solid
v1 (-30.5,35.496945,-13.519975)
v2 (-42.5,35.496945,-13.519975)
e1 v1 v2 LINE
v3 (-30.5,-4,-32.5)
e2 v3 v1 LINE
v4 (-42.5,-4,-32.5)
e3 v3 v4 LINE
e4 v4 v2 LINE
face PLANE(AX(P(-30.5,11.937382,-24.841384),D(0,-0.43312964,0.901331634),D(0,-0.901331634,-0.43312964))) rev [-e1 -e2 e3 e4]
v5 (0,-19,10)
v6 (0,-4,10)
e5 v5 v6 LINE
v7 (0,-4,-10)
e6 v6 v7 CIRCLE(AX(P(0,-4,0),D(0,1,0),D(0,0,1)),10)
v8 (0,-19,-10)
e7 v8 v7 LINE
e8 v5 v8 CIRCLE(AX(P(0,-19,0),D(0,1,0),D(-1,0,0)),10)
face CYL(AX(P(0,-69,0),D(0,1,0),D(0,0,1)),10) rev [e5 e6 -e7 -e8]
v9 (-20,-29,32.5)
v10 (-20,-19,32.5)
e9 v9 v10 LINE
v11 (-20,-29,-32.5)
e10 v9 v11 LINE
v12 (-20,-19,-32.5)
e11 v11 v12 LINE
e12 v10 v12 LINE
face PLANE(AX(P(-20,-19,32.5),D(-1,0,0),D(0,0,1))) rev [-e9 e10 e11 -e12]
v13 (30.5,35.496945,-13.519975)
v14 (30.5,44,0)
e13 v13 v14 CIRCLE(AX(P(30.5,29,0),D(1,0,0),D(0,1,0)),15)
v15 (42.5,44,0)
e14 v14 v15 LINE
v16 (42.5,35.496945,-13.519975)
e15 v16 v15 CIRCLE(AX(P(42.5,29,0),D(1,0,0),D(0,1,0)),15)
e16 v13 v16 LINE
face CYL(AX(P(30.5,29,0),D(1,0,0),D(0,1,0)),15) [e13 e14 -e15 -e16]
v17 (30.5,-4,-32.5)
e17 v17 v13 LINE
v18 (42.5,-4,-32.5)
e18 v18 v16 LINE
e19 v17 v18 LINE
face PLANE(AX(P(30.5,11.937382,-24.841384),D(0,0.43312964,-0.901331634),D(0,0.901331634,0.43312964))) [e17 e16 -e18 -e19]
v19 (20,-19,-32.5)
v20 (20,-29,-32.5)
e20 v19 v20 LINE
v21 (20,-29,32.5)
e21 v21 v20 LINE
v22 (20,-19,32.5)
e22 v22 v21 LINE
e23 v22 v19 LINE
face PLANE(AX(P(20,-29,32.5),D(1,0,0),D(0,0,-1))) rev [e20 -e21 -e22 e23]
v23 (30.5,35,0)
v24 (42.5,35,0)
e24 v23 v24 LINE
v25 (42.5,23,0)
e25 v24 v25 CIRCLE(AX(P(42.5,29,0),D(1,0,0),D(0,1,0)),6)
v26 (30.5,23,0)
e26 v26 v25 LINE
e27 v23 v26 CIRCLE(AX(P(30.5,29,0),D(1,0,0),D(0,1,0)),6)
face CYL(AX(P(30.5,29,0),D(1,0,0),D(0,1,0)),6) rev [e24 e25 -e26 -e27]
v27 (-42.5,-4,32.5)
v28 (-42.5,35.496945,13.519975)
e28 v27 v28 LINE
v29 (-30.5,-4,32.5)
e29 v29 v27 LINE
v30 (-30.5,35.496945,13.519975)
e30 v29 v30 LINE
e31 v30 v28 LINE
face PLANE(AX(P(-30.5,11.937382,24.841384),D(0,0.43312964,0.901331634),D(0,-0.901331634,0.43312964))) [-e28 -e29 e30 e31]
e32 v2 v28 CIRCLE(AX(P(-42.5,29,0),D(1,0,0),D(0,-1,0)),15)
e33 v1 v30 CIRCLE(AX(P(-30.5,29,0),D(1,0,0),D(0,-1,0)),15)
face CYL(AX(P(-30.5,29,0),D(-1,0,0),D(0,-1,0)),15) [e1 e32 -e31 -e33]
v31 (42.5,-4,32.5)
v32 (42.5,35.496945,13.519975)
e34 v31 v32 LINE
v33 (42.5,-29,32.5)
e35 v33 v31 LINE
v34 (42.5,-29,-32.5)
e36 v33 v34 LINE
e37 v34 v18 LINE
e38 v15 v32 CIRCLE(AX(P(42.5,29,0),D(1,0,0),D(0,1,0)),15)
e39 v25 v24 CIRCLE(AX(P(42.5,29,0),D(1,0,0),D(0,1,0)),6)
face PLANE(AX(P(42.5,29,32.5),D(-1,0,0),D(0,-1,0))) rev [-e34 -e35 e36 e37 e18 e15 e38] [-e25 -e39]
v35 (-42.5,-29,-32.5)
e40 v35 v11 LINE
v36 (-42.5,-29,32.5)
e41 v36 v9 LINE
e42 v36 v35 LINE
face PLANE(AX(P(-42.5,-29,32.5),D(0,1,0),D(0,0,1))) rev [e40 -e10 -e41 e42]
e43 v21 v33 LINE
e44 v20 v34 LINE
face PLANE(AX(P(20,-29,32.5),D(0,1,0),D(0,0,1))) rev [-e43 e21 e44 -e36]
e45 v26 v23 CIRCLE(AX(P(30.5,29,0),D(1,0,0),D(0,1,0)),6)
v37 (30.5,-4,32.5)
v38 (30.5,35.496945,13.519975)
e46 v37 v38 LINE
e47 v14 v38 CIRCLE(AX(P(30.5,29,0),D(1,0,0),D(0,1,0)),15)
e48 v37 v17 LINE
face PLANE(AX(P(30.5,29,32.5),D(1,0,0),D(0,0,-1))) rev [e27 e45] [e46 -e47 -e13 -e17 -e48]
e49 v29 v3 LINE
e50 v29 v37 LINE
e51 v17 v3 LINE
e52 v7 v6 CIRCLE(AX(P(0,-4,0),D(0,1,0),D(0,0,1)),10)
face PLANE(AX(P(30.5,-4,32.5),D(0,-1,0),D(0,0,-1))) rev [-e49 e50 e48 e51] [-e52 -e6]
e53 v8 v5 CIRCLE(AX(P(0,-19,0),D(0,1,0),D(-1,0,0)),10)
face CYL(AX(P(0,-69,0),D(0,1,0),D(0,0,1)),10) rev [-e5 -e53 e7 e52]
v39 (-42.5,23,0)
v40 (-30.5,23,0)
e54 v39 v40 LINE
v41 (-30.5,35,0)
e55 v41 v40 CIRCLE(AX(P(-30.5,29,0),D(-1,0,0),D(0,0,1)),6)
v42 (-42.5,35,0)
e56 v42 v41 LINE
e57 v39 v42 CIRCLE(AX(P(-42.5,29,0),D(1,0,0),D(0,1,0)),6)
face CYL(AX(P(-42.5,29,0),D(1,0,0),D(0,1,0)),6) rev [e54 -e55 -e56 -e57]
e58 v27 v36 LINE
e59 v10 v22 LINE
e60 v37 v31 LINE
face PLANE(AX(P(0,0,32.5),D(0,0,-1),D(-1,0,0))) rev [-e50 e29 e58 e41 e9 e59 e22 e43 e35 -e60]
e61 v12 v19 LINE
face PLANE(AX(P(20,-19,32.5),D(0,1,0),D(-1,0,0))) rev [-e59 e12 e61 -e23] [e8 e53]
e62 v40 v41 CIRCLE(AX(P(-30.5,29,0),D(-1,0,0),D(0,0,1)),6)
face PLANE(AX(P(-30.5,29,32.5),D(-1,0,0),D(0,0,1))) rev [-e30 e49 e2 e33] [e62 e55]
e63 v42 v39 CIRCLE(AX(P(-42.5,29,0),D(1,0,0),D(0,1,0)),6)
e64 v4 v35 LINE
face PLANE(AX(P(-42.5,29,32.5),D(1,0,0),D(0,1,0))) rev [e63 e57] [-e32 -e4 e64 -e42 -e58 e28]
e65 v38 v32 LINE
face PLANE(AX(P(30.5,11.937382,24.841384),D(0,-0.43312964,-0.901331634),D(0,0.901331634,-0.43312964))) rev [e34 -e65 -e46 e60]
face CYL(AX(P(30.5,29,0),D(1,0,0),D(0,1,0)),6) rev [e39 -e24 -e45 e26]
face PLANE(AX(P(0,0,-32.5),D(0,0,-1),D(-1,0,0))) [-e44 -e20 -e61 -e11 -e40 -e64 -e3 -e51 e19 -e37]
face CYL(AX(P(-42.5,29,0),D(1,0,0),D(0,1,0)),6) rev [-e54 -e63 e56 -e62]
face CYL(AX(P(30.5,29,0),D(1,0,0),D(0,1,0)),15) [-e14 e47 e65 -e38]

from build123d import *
from build123d.topology import SkipClean

# Parameters (mm, degrees)
BASE_BLOCK_DEPTH     = 32.5
CENTRE_HOLE_SKETCH_R = 10
CENTRE_HOLE_20_DEPTH = 65
LUG_A_BOSS_DEPTH     = 12
LUG_TRIM_CUT_DEPTH   = 102.080413533
LUG_B_BOSS_DEPTH     = 12
PIN_HOLE_SKETCH_R    = 6
PIN_HOLE_CUT_DEPTH   = 102.080413533
LUG_START            = -12
LUG_C_BOSS_DEPTH     = 12
LUG_RIB_A_SKETCH_W   = 61
LUG_RIB_A_SKETCH_H   = 4.481596486
LUG_RIB_A_DEPTH      = 13
LUG_RIB_B_SKETCH_W   = 61
LUG_RIB_B_SKETCH_H   = 4.481596486
LUG_RIB_B_DEPTH      = 13


with BuildPart() as part:
    # Base Profile Sketch → Base Block (new, symmetric)
    with BuildSketch(Plane.XY):
        Polygon((-42.5, 29), (-30.5, 29), (-30.5, -4), (30.5, -4), (30.5, 29), (42.5, 29), (42.5, -29), (20, -29), (20, -19), (-20, -19), (-20, -29), (-42.5, -29), align=None)
    extrude(amount=BASE_BLOCK_DEPTH, both=True)

    # Centre Hole Sketch → Centre Hole Ø20 (cut)
    with BuildSketch(Plane(origin=(0, -4, 0), x_dir=(1, 0, 0), z_dir=(0, 1, 0))):
        with Locations(Location((0, 0, 0), (0, 0, 270))):
            Circle(CENTRE_HOLE_SKETCH_R)
    extrude(amount=-CENTRE_HOLE_20_DEPTH, mode=Mode.SUBTRACT)

    # Lug A Sketch → Lug A Boss (add)
    with BuildSketch(Plane(origin=(42.5, 0, 0), x_dir=(0, 0, -1), z_dir=(1, 0, 0))):
        with BuildLine():
            ThreePointArc((13.519974515, 35.496944598), (0, 44), (-13.519974515, 35.496944598))
            ThreePointArc((-13.519974515, 35.496944598), (-14.625313975, 32.331694935), (-15, 29))
            Line((-15, 29), (-6, 29))
            ThreePointArc((-6, 29), (0, 35), (6, 29))
            Line((6, 29), (15, 29))
            ThreePointArc((15, 29), (14.625313975, 32.331694935), (13.519974515, 35.496944598))
        make_face()
        with BuildLine():
            Line((-6, 29), (-15, 29))
            ThreePointArc((-15, 29), (0, 14), (15, 29))
            Line((15, 29), (6, 29))
            ThreePointArc((6, 29), (0, 23), (-6, 29))
        make_face()
        with BuildLine():
            ThreePointArc((13.519974515, 35.496944598), (0, 44), (-13.519974515, 35.496944598))
            ThreePointArc((-13.519974515, 35.496944598), (-14.625313975, 32.331694935), (-15, 29))
            Line((-15, 29), (-6, 29))
            ThreePointArc((-6, 29), (0, 35), (6, 29))
            Line((6, 29), (15, 29))
            ThreePointArc((15, 29), (14.625313975, 32.331694935), (13.519974515, 35.496944598))
        make_face()
        with BuildLine():
            Line((-6, 29), (-15, 29))
            ThreePointArc((-15, 29), (0, 14), (15, 29))
            Line((15, 29), (6, 29))
            ThreePointArc((6, 29), (0, 23), (-6, 29))
        make_face()
        with BuildLine():
            Line((-16.642043204, 29), (-32.5, -4))
            Line((-32.5, -4), (32.5, -4))
            Line((32.5, -4), (16.642043204, 29))
            Line((16.642043204, 29), (15, 29))
            ThreePointArc((15, 29), (0, 14), (-15, 29))
            Line((-15, 29), (-16.642043204, 29))
        make_face()
        with BuildLine():
            Line((-13.519974515, 35.496944598), (-16.642043204, 29))
            Line((-16.642043204, 29), (-15, 29))
            ThreePointArc((-15, 29), (-14.625313975, 32.331694935), (-13.519974515, 35.496944598))
        make_face()
        with BuildLine():
            Line((15, 29), (16.642043204, 29))
            Line((16.642043204, 29), (13.519974515, 35.496944598))
            ThreePointArc((13.519974515, 35.496944598), (14.625313975, 32.331694935), (15, 29))
        make_face()
    extrude(amount=-LUG_A_BOSS_DEPTH)

    # Lug Trim Sketch → Lug Trim Cut (cut, through all)
    with BuildSketch(Plane(origin=(42.5, 0, 0), x_dir=(0, 0, -1), z_dir=(1, 0, 0))):
        Polygon((-32.5, -17), (-16.642043204, 29), (-32.5, 29), align=None)
        Polygon((32.5, -17), (16.642043204, 29), (32.5, 29), align=None)
    extrude(amount=-LUG_TRIM_CUT_DEPTH, mode=Mode.SUBTRACT)

    # Lug B Sketch → Lug B Boss (add)
    with BuildSketch(Plane(origin=(42.5, 0, 0), x_dir=(0, 0, -1), z_dir=(1, 0, 0))):
        Polygon((-16.642043204, 29), (-32.5, -4), (-32.5, -17), align=None)
        Polygon((32.5, -4), (32.5, -17), (16.642043204, 29), align=None)
    extrude(amount=-LUG_B_BOSS_DEPTH)

    # Pin Hole Sketch → Pin Hole Cut (cut, through all)
    with SkipClean():  # the faces are left unmerged after this step: merging them gives an invalid solid
        with BuildSketch(Plane(origin=(42.5, 0, 0), x_dir=(0, 0, -1), z_dir=(1, 0, 0))):
            with Locations(Location((0, 29, 0), (0, 0, 90))):
                Circle(PIN_HOLE_SKETCH_R)
        extrude(amount=-PIN_HOLE_CUT_DEPTH, mode=Mode.SUBTRACT)

    # Lug C Sketch → Lug C Boss (add)
    with SkipClean():  # the faces are left unmerged after this step: merging them gives an invalid solid
        with BuildSketch(Plane.ZY.offset(42.5).offset(LUG_START)):
            with BuildLine():
                ThreePointArc((13.519974515, 35.496944598), (0, 44), (-13.519974515, 35.496944598))
                ThreePointArc((-13.519974515, 35.496944598), (-14.625313975, 32.331694935), (-15, 29))
                Line((-15, 29), (-6, 29))
                ThreePointArc((-6, 29), (0, 35), (6, 29))
                Line((6, 29), (15, 29))
                ThreePointArc((15, 29), (14.625313975, 32.331694935), (13.519974515, 35.496944598))
            make_face()
            Polygon((-32.5, -4), (-16.642043204, 29), (-32.5, -17), align=None)
            Polygon((32.5, -17), (32.5, -4), (16.642043204, 29), align=None)
            with BuildLine():
                Line((-13.519974515, 35.496944598), (-16.642043204, 29))
                Line((-16.642043204, 29), (-15, 29))
                ThreePointArc((-15, 29), (-14.625313975, 32.331694935), (-13.519974515, 35.496944598))
            make_face()
            with BuildLine():
                Line((16.642043204, 29), (13.519974515, 35.496944598))
                ThreePointArc((13.519974515, 35.496944598), (14.625313975, 32.331694935), (15, 29))
                Line((15, 29), (16.642043204, 29))
            make_face()
        extrude(amount=LUG_C_BOSS_DEPTH)

    # Lug Rib A Sketch → Lug Rib A (add)
    with SkipClean():  # the faces are left unmerged after this step: merging them gives an invalid solid
        with BuildSketch(Plane(origin=(0, -4, 0), x_dir=(1, 0, 0), z_dir=(0, 1, 0))):
            with Locations((0, 30.259201757)):
                Rectangle(LUG_RIB_A_SKETCH_W, LUG_RIB_A_SKETCH_H)
        extrude(amount=-LUG_RIB_A_DEPTH)

    # Lug Rib B Sketch → Lug Rib B (add)
    with SkipClean():  # the faces are left unmerged after this step: merging them gives an invalid solid
        with BuildSketch(Plane(origin=(0, -4, 0), x_dir=(1, 0, 0), z_dir=(0, 1, 0))):
            with Locations((0, -30.259201757)):
                Rectangle(LUG_RIB_B_SKETCH_W, LUG_RIB_B_SKETCH_H)
        extrude(amount=-LUG_RIB_B_DEPTH)


solid = part.part
